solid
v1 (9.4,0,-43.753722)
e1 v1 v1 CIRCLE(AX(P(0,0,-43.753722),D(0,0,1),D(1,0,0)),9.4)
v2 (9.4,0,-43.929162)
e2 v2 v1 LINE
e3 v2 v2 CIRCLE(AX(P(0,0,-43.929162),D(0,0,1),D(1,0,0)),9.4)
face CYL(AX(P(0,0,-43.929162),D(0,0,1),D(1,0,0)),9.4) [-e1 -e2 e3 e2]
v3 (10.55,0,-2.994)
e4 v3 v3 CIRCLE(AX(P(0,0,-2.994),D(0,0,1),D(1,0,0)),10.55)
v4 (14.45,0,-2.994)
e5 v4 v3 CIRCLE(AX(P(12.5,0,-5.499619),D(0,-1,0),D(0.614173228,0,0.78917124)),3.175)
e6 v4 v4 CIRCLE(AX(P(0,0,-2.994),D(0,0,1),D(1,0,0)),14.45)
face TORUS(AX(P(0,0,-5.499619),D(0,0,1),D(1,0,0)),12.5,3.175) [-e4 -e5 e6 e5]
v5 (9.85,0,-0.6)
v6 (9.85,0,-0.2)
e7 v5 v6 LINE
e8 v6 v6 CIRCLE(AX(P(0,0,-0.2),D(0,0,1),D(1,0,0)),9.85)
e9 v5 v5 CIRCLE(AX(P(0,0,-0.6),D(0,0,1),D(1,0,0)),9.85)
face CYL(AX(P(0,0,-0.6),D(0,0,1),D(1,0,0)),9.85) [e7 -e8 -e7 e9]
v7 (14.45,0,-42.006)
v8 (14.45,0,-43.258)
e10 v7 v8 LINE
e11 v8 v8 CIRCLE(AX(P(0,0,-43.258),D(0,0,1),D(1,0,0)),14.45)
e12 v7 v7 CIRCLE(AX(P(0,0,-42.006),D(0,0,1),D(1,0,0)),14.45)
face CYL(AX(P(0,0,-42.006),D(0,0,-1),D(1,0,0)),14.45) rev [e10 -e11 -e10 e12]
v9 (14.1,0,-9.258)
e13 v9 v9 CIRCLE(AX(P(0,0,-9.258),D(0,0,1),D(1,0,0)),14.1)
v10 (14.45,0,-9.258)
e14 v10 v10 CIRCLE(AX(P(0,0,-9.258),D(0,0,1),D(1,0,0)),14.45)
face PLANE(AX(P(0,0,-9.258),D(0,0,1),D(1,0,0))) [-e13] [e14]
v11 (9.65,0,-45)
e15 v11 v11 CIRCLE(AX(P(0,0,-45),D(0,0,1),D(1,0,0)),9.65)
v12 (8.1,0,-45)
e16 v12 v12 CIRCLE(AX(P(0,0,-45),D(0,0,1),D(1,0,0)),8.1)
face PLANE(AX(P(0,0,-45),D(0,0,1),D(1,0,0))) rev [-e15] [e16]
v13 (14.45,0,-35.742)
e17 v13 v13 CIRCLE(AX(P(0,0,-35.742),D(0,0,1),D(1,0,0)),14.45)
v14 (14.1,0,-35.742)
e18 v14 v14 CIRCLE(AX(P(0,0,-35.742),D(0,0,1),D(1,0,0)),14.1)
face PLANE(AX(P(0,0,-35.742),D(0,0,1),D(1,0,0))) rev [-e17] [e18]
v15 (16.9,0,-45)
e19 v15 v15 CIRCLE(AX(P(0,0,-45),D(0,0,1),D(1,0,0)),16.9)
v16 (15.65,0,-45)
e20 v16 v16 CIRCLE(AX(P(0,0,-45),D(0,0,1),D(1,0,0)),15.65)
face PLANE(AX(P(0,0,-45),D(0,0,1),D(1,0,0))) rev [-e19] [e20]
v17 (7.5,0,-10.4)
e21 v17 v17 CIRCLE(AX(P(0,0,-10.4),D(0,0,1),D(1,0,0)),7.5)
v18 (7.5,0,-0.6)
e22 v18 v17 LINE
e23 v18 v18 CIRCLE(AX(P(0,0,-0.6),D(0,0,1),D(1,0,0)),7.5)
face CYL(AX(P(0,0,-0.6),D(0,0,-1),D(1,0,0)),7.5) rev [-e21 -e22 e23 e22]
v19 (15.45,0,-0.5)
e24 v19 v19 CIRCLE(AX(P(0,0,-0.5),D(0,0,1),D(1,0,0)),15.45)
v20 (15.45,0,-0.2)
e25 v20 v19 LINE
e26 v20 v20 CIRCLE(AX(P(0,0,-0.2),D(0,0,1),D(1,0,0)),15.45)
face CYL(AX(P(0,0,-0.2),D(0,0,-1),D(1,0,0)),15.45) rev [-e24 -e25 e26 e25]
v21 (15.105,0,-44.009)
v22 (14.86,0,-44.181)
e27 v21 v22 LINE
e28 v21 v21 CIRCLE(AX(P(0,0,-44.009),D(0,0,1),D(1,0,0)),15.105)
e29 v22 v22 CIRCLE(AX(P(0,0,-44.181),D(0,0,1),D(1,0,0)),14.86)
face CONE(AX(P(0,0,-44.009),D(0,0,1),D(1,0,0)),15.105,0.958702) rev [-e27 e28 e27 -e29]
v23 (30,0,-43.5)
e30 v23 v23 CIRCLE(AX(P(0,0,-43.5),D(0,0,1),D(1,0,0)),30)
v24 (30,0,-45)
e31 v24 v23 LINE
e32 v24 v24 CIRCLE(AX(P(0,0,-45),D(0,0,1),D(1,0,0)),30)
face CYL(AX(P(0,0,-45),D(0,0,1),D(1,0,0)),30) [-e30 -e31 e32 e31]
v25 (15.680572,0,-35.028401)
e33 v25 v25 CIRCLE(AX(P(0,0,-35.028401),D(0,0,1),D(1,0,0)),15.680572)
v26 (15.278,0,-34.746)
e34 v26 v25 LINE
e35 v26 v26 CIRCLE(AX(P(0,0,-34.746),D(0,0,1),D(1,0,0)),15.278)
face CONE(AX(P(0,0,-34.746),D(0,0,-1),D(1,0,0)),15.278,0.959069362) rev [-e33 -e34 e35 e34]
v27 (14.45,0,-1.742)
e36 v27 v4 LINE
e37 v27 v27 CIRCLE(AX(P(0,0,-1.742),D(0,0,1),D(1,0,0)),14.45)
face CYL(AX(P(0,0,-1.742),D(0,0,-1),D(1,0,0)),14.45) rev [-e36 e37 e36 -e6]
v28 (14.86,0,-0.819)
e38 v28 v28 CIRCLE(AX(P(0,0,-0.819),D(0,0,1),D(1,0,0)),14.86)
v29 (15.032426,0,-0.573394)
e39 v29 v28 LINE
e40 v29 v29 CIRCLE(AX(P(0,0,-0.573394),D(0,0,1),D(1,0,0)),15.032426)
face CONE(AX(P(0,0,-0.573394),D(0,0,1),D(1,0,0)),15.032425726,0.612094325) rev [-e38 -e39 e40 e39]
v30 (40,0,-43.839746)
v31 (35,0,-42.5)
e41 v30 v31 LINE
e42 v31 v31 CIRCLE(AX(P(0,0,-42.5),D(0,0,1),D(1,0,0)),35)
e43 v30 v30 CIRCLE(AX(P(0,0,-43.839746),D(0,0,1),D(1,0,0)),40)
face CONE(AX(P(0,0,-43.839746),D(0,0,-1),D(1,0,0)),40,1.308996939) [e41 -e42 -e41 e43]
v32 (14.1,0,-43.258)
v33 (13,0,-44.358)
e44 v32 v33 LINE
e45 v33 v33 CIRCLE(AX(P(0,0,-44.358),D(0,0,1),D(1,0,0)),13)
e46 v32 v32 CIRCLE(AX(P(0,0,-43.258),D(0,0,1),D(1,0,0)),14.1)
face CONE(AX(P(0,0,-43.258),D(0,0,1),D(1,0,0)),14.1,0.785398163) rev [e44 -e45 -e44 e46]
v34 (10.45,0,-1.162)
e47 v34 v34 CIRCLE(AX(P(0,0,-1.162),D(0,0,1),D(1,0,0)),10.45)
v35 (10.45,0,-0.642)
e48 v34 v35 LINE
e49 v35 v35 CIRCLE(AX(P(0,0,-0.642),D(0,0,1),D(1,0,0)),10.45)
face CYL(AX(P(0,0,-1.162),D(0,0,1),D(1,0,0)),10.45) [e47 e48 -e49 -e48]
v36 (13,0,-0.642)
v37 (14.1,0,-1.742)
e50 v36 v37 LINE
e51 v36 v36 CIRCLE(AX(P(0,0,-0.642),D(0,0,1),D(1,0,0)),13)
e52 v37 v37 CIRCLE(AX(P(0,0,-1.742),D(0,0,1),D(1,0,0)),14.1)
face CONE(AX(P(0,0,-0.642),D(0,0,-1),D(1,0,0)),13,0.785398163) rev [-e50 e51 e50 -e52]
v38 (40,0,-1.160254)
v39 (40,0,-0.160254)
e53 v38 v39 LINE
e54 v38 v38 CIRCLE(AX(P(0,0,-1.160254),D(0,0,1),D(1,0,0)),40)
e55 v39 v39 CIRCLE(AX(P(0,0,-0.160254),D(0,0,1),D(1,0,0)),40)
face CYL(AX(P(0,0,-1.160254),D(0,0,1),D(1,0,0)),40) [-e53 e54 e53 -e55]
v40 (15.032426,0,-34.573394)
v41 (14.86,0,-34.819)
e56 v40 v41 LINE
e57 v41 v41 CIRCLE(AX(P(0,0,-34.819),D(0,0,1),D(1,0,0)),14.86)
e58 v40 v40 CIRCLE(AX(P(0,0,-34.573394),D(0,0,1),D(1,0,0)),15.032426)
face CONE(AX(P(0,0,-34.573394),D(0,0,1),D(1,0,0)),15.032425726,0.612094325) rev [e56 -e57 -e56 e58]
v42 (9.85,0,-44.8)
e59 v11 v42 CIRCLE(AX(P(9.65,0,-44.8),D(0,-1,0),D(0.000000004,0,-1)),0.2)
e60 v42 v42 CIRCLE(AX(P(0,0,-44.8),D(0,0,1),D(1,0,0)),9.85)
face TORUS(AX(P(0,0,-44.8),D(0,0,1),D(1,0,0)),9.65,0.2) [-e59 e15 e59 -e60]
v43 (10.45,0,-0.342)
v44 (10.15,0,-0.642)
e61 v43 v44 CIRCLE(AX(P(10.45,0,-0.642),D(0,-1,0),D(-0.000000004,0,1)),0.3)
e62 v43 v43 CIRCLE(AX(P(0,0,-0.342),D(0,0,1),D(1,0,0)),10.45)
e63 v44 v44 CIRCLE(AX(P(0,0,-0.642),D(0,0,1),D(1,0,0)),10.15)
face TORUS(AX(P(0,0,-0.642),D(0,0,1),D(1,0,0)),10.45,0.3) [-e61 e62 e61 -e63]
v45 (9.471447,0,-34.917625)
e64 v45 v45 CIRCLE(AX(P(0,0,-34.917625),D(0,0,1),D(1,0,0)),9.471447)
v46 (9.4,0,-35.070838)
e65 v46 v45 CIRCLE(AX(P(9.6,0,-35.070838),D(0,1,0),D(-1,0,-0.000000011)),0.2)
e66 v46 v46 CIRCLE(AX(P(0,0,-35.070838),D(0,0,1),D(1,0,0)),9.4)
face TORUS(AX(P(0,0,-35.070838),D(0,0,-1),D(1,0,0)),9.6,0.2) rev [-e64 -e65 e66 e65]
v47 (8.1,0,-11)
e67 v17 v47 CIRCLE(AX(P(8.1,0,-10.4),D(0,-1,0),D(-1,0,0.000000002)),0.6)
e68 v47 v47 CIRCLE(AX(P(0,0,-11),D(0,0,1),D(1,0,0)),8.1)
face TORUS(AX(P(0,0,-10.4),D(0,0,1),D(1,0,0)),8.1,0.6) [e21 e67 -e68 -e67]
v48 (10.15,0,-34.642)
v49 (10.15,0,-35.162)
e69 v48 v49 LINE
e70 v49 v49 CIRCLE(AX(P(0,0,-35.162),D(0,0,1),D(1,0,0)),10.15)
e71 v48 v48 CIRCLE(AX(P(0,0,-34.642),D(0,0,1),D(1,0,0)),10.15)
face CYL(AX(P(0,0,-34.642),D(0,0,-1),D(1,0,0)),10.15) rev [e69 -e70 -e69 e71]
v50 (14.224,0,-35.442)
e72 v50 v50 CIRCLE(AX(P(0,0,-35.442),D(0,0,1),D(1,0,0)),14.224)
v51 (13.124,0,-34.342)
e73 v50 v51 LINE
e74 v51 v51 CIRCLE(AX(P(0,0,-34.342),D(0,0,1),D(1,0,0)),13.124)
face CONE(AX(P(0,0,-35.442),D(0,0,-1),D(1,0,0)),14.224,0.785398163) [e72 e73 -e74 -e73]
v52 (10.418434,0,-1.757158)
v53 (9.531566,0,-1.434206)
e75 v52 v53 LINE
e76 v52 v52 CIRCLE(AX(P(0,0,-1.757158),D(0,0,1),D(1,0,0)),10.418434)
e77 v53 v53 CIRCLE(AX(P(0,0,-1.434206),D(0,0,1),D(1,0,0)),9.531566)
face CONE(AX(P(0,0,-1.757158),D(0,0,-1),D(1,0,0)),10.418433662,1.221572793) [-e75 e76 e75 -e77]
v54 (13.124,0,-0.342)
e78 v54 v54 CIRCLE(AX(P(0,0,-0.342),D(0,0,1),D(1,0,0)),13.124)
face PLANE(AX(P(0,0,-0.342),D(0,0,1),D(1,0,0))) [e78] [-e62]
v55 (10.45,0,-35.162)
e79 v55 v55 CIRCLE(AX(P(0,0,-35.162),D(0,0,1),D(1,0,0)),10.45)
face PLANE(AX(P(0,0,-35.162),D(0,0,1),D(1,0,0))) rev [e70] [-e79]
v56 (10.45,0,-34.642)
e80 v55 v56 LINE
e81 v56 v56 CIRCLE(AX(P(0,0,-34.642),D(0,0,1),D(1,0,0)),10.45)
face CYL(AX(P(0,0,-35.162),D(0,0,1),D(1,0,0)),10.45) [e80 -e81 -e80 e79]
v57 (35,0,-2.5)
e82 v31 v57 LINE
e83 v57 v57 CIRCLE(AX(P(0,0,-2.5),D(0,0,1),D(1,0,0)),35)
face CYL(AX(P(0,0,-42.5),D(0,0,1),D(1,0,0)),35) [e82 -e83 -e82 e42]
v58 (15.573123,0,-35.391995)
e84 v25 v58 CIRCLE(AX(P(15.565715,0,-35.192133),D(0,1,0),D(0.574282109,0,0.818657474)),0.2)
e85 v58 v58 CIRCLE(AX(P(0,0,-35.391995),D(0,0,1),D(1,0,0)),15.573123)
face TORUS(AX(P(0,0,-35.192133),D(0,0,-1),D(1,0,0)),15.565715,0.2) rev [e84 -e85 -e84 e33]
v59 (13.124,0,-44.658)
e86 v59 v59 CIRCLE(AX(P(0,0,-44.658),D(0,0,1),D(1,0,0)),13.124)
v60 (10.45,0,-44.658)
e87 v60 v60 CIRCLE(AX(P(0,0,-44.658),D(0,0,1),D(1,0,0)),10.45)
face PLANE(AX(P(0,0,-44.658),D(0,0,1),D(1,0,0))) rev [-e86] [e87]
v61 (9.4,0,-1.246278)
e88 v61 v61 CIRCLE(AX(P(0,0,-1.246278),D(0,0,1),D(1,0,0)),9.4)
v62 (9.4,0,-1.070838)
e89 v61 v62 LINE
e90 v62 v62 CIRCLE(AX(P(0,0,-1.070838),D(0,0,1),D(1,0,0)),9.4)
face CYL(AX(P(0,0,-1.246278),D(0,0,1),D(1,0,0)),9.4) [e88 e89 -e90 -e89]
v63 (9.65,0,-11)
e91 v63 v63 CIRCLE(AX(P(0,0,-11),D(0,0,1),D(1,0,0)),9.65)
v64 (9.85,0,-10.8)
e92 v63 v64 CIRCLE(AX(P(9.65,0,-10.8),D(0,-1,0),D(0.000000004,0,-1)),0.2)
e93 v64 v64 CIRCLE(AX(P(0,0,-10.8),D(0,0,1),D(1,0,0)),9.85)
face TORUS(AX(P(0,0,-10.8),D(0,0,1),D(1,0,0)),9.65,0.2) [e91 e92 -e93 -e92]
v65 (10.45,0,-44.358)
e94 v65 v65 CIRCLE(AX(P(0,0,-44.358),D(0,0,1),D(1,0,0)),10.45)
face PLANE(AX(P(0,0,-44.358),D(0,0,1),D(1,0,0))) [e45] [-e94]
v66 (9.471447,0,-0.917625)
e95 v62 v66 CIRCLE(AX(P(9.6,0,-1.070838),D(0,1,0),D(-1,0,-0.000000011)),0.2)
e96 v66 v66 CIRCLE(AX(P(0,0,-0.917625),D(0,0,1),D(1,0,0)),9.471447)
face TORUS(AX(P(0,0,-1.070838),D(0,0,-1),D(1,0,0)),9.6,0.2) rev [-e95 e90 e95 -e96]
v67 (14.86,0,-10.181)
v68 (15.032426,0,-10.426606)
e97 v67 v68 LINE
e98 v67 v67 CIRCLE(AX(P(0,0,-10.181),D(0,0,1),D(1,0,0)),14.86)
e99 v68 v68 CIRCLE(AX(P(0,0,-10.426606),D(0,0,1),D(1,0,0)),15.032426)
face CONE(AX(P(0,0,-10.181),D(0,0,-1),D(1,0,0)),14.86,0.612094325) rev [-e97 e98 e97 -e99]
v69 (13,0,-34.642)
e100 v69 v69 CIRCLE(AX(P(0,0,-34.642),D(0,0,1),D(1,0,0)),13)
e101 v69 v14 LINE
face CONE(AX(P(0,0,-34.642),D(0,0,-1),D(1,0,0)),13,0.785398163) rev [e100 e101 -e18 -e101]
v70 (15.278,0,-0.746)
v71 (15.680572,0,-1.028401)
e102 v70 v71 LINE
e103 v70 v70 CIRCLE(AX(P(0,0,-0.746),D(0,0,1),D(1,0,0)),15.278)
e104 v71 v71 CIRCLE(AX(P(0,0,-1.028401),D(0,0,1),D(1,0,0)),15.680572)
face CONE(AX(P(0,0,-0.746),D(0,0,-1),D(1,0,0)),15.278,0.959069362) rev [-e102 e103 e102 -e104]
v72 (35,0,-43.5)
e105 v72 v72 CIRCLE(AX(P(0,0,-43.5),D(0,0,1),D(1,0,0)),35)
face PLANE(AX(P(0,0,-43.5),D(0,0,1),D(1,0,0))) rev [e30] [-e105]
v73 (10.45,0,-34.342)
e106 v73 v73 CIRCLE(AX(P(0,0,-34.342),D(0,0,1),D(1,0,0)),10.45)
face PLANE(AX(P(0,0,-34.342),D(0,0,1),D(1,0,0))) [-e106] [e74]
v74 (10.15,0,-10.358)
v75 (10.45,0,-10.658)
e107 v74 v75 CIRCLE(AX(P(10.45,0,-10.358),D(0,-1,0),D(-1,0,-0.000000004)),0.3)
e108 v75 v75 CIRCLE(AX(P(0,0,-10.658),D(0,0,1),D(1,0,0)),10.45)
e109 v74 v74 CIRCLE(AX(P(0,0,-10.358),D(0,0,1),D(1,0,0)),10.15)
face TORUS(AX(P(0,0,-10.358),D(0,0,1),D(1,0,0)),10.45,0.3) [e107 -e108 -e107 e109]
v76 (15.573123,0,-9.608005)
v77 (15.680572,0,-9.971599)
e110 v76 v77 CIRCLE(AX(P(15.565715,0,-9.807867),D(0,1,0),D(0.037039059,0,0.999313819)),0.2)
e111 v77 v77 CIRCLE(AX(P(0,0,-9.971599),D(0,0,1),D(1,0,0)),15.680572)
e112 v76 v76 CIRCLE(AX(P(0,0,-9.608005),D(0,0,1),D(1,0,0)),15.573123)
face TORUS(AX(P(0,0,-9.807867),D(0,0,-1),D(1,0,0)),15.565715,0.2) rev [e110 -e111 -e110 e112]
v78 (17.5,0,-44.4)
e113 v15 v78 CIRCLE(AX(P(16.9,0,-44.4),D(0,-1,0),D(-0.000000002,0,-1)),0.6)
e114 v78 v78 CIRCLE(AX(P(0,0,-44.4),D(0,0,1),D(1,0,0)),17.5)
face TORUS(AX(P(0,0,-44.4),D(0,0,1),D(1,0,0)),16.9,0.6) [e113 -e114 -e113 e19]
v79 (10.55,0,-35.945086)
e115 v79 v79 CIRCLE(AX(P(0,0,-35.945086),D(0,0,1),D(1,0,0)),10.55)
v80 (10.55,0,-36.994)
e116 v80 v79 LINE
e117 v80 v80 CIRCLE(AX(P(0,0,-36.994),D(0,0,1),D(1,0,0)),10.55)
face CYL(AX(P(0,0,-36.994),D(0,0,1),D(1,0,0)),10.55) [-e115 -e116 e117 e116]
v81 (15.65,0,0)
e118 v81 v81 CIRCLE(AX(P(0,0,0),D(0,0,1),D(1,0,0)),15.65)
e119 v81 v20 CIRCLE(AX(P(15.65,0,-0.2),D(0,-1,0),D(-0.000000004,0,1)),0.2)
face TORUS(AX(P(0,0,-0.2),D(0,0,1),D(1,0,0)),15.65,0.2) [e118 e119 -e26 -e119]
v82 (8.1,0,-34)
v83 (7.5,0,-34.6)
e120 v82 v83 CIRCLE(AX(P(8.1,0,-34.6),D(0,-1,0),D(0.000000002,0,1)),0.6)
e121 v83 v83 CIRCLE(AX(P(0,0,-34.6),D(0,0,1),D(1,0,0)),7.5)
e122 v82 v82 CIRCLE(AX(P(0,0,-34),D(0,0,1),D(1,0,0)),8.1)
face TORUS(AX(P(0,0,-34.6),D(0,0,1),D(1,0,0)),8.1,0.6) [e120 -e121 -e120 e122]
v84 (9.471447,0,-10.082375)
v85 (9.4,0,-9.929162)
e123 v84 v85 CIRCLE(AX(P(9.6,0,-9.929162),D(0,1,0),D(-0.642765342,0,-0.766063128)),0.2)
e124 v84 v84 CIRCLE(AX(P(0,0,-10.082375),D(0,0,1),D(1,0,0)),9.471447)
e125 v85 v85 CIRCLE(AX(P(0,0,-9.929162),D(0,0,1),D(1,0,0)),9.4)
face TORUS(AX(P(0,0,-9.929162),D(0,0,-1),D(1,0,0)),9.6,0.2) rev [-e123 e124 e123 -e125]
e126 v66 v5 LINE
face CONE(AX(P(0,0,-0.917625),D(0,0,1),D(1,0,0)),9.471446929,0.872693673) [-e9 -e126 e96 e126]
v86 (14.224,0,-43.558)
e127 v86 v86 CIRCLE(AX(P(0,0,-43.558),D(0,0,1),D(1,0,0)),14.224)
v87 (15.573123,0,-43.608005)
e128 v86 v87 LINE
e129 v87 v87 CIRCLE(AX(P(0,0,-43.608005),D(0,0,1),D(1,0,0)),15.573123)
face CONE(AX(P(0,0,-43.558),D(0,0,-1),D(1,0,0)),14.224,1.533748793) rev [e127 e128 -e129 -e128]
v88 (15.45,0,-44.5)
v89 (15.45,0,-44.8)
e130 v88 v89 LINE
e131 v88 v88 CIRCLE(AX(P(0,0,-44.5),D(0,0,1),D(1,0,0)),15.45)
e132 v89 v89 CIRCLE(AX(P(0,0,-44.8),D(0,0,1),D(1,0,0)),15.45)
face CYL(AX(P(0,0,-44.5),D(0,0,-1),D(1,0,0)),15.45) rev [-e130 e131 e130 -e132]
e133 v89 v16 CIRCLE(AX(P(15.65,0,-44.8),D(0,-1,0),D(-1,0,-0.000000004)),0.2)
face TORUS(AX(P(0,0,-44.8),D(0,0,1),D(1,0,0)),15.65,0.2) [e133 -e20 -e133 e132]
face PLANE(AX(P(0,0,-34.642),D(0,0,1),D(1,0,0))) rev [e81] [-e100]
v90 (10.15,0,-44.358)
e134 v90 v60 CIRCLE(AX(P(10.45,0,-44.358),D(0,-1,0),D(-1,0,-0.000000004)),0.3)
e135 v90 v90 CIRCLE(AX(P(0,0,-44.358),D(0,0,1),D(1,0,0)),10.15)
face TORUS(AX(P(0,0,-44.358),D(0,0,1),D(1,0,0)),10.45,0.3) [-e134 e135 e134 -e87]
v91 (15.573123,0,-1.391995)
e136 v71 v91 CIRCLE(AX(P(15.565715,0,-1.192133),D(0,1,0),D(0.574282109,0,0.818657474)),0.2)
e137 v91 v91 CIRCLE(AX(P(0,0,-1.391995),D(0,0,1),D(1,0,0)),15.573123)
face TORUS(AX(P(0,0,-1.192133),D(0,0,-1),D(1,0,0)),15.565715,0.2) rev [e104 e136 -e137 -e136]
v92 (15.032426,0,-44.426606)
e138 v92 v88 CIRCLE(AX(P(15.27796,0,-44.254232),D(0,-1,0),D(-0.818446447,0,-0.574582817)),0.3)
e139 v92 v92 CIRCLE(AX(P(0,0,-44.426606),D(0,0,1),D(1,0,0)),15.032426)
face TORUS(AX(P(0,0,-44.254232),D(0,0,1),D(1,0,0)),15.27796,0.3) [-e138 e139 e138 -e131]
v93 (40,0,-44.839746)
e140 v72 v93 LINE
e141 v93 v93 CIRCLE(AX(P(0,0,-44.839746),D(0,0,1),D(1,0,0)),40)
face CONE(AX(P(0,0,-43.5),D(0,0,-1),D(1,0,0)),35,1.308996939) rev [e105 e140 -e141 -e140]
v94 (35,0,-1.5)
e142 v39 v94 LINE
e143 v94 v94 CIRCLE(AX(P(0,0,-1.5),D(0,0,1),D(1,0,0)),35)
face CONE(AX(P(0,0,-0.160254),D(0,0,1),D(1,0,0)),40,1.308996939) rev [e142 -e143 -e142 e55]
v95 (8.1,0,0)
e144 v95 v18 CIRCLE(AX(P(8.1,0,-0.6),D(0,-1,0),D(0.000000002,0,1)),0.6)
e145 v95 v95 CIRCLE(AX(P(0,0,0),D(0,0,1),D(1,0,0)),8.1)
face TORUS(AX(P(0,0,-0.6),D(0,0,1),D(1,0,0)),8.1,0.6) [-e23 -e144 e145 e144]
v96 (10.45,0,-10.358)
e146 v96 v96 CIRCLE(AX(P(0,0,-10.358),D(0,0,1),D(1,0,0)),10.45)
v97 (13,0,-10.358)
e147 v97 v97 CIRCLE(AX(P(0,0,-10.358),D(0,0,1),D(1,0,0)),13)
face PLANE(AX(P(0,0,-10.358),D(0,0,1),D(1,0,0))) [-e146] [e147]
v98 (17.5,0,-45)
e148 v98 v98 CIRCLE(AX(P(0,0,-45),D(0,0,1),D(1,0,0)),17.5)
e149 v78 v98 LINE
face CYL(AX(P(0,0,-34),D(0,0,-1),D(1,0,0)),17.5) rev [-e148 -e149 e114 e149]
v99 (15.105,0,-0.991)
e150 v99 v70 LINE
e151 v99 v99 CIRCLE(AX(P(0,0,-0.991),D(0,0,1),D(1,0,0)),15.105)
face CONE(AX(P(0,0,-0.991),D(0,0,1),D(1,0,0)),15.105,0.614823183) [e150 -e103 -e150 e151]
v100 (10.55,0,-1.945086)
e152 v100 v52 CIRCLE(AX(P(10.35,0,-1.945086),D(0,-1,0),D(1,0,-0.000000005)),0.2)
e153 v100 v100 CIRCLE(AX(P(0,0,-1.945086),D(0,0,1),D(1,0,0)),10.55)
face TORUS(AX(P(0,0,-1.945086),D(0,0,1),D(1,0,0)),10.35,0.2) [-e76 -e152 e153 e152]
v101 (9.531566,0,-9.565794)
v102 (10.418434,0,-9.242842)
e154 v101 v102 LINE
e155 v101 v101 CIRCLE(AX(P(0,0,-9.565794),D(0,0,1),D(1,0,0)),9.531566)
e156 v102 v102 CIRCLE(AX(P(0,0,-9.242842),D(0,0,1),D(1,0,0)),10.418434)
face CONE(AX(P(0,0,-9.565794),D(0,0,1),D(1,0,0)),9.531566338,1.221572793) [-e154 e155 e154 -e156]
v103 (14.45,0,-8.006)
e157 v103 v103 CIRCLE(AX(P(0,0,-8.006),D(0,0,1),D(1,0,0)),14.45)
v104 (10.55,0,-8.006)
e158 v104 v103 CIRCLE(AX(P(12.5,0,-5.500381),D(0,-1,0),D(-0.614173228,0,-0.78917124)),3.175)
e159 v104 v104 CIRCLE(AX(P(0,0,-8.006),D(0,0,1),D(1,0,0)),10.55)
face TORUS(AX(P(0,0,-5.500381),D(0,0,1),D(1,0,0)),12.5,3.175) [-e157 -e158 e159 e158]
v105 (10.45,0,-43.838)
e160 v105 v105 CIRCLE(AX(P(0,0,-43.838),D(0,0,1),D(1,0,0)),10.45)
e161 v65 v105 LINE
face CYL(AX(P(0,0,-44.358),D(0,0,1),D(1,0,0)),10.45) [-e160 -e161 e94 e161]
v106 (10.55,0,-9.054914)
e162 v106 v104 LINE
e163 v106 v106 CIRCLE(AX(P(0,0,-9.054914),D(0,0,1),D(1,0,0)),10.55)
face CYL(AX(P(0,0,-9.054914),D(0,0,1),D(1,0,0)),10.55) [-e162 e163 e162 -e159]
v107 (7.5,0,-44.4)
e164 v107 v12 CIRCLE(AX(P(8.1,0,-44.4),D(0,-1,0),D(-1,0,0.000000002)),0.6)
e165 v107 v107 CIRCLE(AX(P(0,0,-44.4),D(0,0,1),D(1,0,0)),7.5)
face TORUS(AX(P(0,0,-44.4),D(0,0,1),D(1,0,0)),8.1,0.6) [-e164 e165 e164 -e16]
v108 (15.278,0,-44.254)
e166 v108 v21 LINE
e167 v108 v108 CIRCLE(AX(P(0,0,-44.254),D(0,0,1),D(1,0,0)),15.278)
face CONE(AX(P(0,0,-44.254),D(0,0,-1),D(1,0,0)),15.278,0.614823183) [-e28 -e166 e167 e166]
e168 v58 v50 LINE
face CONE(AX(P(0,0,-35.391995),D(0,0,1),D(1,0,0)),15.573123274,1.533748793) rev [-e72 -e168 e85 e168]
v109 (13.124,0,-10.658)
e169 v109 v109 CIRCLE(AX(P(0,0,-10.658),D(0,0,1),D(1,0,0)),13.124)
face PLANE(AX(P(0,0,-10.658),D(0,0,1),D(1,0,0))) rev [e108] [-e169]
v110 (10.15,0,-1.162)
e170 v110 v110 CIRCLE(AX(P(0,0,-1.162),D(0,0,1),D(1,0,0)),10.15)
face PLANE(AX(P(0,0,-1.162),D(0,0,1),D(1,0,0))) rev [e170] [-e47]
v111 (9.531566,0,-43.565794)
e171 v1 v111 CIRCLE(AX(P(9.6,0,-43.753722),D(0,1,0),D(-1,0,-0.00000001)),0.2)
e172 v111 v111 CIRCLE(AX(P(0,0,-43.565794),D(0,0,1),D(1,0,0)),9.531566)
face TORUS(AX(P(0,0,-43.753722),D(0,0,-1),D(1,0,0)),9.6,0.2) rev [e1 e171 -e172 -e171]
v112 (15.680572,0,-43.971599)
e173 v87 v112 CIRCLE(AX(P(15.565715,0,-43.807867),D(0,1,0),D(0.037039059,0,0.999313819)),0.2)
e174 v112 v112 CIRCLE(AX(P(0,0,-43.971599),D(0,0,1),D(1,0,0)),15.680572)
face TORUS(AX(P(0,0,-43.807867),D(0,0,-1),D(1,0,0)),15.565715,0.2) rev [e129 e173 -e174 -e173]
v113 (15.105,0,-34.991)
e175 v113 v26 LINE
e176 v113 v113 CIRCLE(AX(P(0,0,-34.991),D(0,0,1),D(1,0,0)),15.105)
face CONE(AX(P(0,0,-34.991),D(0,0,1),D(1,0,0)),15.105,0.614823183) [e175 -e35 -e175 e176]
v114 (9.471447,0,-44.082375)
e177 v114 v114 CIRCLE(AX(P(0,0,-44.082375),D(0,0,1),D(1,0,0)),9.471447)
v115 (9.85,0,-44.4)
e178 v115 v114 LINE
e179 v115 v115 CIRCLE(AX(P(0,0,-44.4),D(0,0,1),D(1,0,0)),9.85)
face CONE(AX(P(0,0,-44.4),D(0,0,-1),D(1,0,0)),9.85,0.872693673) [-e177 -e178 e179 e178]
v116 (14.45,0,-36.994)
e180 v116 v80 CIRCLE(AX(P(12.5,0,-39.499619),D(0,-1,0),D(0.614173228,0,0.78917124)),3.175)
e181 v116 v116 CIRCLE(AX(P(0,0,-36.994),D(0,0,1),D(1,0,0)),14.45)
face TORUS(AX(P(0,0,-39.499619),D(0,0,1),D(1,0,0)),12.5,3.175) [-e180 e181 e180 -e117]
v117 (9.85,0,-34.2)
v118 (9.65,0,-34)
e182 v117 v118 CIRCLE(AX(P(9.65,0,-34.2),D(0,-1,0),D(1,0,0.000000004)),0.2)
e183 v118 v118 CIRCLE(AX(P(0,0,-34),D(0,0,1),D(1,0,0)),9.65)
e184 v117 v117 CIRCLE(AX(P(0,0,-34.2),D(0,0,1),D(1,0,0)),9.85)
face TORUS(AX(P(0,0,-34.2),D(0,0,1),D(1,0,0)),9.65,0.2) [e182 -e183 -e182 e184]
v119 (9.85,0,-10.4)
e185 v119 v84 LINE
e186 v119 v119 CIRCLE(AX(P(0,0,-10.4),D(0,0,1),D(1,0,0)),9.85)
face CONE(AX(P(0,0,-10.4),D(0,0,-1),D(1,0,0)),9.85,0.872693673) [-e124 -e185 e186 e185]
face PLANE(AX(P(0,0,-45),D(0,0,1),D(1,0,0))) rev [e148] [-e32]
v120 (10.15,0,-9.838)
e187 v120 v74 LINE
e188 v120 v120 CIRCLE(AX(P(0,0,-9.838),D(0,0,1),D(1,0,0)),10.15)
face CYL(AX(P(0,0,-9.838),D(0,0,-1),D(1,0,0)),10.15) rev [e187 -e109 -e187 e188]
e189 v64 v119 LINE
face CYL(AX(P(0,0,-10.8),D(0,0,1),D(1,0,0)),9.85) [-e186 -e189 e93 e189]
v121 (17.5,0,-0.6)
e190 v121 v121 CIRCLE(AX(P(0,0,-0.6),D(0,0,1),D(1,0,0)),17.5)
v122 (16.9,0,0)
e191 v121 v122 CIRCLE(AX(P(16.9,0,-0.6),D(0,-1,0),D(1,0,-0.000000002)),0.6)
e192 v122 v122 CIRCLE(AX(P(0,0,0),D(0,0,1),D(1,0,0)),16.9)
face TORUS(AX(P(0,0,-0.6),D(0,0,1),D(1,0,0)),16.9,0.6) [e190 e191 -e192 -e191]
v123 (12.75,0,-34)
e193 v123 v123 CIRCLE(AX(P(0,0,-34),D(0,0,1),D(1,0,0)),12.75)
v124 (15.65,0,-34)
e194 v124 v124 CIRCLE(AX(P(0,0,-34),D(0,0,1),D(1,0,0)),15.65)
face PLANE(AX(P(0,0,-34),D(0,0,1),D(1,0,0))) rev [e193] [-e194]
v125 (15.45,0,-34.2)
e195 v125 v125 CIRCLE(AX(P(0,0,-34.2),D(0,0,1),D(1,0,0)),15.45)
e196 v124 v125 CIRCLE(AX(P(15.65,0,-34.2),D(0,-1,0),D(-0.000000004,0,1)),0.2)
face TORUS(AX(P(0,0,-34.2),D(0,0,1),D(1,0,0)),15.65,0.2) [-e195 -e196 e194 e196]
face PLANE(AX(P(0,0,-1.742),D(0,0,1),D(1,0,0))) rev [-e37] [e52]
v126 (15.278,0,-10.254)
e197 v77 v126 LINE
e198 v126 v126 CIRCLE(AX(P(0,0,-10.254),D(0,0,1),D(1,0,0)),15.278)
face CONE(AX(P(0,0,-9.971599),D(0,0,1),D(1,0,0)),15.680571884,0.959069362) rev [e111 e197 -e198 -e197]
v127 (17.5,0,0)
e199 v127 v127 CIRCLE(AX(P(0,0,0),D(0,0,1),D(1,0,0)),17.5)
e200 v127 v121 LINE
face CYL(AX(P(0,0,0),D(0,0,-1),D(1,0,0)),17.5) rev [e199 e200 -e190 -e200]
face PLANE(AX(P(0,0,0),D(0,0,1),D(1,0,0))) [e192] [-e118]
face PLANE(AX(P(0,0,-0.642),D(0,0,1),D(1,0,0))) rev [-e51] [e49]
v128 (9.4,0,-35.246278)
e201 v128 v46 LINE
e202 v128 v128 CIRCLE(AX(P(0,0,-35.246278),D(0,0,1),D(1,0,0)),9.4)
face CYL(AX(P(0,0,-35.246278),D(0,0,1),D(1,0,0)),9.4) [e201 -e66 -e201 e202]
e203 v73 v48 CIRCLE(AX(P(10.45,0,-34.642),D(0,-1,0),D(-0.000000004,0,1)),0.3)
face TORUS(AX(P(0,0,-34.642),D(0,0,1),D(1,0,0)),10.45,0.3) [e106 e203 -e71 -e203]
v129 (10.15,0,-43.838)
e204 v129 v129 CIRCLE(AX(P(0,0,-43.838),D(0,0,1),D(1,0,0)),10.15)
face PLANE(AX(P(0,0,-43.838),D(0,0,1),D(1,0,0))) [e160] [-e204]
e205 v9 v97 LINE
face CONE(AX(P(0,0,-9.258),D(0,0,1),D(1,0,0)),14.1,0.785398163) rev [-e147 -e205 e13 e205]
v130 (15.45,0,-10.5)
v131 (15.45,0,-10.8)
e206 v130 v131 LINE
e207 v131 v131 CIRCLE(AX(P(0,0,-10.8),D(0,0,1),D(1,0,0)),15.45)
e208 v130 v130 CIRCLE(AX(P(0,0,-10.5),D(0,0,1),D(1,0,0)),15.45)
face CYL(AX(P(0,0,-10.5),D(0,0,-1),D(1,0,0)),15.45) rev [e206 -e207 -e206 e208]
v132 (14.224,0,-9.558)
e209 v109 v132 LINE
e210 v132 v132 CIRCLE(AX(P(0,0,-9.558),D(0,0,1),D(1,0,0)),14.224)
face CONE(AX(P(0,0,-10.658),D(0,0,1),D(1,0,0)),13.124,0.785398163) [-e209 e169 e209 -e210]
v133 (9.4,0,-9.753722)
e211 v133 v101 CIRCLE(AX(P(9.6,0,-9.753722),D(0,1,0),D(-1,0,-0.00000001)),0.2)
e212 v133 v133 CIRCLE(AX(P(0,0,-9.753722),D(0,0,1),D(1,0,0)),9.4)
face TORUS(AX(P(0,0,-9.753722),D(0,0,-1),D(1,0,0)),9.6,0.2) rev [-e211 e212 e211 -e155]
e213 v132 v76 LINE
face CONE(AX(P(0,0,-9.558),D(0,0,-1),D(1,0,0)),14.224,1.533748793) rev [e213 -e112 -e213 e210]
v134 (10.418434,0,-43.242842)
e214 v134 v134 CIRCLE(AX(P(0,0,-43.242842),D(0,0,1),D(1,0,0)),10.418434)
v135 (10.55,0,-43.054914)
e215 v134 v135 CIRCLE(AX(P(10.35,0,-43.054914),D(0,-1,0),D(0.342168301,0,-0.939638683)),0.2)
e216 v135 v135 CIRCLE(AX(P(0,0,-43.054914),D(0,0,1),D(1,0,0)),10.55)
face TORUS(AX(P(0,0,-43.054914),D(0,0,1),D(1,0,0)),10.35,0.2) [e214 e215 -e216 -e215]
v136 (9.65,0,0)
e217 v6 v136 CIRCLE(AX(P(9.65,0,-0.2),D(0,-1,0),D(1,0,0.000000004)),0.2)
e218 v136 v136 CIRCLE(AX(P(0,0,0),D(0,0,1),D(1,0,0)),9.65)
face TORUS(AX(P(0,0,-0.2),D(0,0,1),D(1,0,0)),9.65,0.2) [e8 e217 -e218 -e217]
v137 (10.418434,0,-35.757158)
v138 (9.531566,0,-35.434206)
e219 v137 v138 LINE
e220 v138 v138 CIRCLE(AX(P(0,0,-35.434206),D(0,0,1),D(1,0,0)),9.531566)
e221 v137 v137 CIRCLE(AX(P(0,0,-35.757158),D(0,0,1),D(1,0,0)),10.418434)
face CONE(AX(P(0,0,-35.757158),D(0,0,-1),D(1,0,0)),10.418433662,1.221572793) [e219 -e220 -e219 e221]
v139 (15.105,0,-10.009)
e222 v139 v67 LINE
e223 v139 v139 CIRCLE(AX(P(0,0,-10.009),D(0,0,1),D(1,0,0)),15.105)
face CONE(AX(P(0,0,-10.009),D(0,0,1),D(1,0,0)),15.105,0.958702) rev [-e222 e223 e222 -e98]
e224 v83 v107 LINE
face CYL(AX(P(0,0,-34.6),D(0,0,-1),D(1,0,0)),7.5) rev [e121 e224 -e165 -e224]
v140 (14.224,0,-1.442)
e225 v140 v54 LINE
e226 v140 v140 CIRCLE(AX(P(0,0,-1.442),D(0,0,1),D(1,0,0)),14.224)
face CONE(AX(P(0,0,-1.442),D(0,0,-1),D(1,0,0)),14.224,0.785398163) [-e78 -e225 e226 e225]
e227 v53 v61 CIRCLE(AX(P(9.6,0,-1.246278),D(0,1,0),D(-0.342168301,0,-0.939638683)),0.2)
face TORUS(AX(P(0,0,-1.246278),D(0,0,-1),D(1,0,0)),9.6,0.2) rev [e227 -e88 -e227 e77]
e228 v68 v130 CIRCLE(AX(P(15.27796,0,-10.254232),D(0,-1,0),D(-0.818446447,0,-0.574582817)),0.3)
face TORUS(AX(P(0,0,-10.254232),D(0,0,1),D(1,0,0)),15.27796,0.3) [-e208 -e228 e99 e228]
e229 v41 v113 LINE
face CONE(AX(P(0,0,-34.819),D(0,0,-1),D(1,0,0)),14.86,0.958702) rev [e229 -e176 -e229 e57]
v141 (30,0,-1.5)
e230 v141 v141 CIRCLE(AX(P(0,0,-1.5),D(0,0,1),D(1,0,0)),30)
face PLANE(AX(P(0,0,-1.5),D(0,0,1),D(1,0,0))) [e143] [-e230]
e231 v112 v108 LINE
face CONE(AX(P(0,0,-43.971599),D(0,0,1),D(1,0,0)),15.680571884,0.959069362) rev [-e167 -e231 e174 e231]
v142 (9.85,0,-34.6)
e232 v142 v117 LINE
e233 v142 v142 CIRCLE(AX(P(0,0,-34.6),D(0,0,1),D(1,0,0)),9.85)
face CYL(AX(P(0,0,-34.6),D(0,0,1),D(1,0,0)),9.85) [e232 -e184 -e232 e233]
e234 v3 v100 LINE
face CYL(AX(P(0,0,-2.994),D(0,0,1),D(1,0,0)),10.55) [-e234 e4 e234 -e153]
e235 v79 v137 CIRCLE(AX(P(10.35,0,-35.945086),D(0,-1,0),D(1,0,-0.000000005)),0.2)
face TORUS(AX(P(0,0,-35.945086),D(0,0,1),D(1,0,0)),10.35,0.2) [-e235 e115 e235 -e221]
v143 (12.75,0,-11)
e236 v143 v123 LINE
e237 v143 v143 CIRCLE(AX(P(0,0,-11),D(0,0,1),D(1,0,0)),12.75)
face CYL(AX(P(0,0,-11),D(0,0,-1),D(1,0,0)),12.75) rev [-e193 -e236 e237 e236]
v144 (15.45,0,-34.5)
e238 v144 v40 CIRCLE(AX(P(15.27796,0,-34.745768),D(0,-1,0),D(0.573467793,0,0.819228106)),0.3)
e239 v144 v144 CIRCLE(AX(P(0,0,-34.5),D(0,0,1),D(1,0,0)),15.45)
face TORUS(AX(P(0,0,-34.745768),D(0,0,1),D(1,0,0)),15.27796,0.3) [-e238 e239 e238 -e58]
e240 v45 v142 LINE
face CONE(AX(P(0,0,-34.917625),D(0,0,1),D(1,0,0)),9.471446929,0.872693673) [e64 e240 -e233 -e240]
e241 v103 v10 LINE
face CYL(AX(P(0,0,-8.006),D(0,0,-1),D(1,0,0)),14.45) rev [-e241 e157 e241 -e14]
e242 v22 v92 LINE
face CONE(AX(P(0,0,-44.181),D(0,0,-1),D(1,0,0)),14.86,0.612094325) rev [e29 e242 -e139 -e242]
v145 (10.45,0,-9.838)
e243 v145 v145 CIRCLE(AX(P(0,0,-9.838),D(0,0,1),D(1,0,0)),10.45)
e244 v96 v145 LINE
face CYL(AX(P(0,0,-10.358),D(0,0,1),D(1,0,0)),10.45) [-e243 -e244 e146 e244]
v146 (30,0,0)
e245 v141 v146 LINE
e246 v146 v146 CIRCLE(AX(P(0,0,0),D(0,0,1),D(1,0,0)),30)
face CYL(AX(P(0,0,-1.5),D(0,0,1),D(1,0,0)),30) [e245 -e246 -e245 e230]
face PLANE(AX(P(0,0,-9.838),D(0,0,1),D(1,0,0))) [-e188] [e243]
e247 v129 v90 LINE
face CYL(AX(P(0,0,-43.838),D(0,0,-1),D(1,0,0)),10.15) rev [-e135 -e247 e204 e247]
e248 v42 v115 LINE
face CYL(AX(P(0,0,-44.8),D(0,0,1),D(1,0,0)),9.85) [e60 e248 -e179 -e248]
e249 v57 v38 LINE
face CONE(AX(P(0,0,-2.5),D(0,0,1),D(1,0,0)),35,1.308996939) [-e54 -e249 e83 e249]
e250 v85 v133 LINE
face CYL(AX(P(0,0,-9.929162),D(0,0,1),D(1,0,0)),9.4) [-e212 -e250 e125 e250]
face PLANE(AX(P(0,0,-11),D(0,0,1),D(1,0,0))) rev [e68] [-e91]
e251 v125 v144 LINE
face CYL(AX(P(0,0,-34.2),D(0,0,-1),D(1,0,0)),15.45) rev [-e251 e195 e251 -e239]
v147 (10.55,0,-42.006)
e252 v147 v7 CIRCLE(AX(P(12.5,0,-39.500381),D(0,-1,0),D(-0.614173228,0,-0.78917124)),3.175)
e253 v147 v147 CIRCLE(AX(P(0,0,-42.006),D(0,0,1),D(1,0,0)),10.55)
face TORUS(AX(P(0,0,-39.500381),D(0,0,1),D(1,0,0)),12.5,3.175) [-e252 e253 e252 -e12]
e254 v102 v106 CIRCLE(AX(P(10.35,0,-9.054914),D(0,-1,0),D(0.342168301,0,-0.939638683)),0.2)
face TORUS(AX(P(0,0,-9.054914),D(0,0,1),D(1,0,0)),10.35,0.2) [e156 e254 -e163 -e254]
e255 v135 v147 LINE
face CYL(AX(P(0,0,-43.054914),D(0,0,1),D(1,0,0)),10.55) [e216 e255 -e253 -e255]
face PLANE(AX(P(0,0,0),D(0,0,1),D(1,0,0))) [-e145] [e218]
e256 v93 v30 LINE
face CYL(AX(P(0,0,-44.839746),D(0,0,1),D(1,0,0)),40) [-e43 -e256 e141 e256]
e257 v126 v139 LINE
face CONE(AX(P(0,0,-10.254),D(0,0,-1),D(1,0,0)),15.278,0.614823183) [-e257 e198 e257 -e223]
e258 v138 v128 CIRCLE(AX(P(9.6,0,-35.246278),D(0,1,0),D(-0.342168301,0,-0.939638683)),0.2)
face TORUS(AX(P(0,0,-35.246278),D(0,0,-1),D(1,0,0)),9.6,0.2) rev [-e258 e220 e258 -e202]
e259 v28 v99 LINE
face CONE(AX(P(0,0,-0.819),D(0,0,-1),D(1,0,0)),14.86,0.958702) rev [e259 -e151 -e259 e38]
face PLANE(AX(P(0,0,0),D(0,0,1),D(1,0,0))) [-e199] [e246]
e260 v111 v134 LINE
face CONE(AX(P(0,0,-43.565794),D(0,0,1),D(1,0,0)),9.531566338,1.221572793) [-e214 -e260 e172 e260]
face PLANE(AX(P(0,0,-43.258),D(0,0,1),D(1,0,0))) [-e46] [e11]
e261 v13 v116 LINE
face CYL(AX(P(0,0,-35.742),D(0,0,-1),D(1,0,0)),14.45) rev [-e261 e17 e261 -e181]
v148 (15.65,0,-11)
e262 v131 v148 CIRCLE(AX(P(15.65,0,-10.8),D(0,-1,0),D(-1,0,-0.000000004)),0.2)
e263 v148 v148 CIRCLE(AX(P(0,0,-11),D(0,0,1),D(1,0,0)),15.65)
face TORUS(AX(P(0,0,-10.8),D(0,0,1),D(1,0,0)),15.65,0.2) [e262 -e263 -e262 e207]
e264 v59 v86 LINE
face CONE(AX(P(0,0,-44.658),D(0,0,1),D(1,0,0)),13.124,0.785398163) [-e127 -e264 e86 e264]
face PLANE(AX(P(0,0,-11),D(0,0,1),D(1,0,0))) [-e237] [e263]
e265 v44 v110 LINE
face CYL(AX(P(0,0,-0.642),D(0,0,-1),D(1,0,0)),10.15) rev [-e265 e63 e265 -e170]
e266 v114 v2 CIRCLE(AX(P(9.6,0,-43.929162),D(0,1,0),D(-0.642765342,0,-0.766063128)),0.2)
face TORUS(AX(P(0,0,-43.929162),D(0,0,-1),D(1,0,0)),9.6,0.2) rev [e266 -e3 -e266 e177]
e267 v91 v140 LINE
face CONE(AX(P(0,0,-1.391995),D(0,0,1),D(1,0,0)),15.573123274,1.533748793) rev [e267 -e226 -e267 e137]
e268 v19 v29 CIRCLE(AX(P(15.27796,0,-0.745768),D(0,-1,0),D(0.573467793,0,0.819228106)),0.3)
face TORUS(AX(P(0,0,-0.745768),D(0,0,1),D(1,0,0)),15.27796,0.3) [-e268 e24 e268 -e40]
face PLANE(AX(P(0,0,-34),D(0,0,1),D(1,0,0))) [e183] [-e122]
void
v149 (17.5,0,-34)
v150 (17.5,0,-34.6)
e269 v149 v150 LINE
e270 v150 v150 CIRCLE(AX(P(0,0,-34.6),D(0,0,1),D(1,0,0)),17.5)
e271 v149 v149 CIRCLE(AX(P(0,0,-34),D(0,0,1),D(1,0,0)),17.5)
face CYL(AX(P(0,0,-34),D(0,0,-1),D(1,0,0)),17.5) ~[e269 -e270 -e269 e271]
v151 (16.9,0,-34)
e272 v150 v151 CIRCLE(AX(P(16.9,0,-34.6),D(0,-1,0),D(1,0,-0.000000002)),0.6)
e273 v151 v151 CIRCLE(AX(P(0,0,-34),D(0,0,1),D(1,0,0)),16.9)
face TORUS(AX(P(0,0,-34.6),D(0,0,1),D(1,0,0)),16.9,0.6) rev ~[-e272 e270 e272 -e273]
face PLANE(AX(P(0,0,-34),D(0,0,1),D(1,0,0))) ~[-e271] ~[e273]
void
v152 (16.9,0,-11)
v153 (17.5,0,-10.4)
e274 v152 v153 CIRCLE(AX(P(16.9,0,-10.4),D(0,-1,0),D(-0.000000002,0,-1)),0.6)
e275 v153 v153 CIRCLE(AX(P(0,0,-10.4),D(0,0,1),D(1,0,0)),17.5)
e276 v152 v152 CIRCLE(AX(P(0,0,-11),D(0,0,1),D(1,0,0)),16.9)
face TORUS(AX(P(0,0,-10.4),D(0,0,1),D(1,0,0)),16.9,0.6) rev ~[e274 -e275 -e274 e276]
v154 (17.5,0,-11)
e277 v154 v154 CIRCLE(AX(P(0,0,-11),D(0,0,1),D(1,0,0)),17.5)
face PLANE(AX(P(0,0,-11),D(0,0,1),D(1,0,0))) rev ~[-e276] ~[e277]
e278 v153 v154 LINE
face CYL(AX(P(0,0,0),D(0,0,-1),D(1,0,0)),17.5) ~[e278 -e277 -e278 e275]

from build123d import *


with BuildPart() as part:
    # 草图1 → 旋转1 (revolve)
    with BuildSketch(Plane(origin=(0, 0, 0), x_dir=(0, 0, -1), z_dir=(1, 0, 0)), mode=Mode.PRIVATE) as revolve_1_sk:
        Polygon((0, 17.5), (11, 17.5), (11, 12.75), (34, 12.75), (34, 17.5), (45, 17.5), (45, 30), (43.5, 30), (43.5, 35), (44.839745962, 40), (43.839745962, 40), (42.5, 35), (2.5, 35), (1.160254038, 40), (0.160254038, 40), (1.5, 35), (1.5, 30), (0, 30), align=None)
    revolve(revolve_1_sk.sketch.rotate(Axis((0, 0, -45), (0, 0, 1)), 270), axis=Axis((0, 0, -45), (0, 0, 1)))

    # 草图2 → 旋转2 (revolve)
    with BuildSketch(Plane(origin=(0, 0, 0), x_dir=(0, 0, -1), z_dir=(1, 0, 0)), mode=Mode.PRIVATE) as revolve_2_sk:
        with BuildLine():
            Line((0.2, 15.45), (0.5, 15.45))
            ThreePointArc((0.5, 15.45), (0.45029759, 15.226027188), (0.573393587, 15.032425726))
            Line((0.573393587, 15.032425726), (0.819, 14.86))
            Line((0.819, 14.86), (0.991, 15.105))
            Line((0.991, 15.105), (0.746, 15.278))
            Line((0.746, 15.278), (1.028401172, 15.680571884))
            ThreePointArc((1.028401172, 15.680571884), (1.24881307, 15.757515702), (1.391995431, 15.573123274))
            Line((1.391995431, 15.573123274), (1.442, 14.224))
            Line((1.442, 14.224), (0.342, 13.124))
            Line((0.342, 13.124), (0.342, 10.45))
            ThreePointArc((0.342, 10.45), (0.429867966, 10.237867966), (0.642, 10.15))
            Line((0.642, 10.15), (1.162, 10.15))
            Line((1.162, 10.15), (1.162, 10.45))
            Line((1.162, 10.45), (0.642, 10.45))
            Line((0.642, 10.45), (0.642, 13))
            Line((0.642, 13), (1.742, 14.1))
            Line((1.742, 14.1), (1.742, 14.45))
            Line((1.742, 14.45), (2.994, 14.45))
            ThreePointArc((2.994, 14.45), (2.324618686, 12.5), (2.994, 10.55))
            Line((2.994, 10.55), (1.945085653, 10.55))
            ThreePointArc((1.945085653, 10.55), (1.830383283, 10.513839453), (1.757157918, 10.418433662))
            Line((1.757157918, 10.418433662), (1.434206231, 9.531566338))
            ThreePointArc((1.434206231, 9.531566338), (1.360980866, 9.436160547), (1.246278495, 9.4))
            Line((1.246278495, 9.4), (1.070837627, 9.4))
            ThreePointArc((1.070837627, 9.4), (0.986311342, 9.41873967), (0.917625005, 9.471446929))
            Line((0.917625005, 9.471446929), (0.6, 9.85))
            Line((0.6, 9.85), (0.2, 9.85))
            ThreePointArc((0.2, 9.85), (0.058578644, 9.791421356), (0, 9.65))
            Line((0, 9.65), (0, 8.1))
            ThreePointArc((0, 8.1), (0.175735931, 7.675735931), (0.6, 7.5))
            Line((0.6, 7.5), (10.4, 7.5))
            ThreePointArc((10.4, 7.5), (10.824264069, 7.675735931), (11, 8.1))
            Line((11, 8.1), (11, 9.65))
            ThreePointArc((11, 9.65), (10.941421356, 9.791421356), (10.8, 9.85))
            Line((10.8, 9.85), (10.4, 9.85))
            Line((10.4, 9.85), (10.082374995, 9.471446929))
            ThreePointArc((10.082374995, 9.471446929), (10.013688658, 9.41873967), (9.929162373, 9.4))
            Line((9.929162373, 9.4), (9.753721505, 9.4))
            ThreePointArc((9.753721505, 9.4), (9.639019134, 9.436160547), (9.565793769, 9.531566338))
            Line((9.565793769, 9.531566338), (9.242842082, 10.418433662))
            ThreePointArc((9.242842082, 10.418433662), (9.169616717, 10.513839453), (9.054914347, 10.55))
            Line((9.054914347, 10.55), (8.006, 10.55))
            ThreePointArc((8.006, 10.55), (8.675381314, 12.5), (8.006, 14.45))
            Line((8.006, 14.45), (9.258, 14.45))
            Line((9.258, 14.45), (9.258, 14.1))
            Line((9.258, 14.1), (10.358, 13))
            Line((10.358, 13), (10.358, 10.45))
            Line((10.358, 10.45), (9.838, 10.45))
            Line((9.838, 10.45), (9.838, 10.15))
            Line((9.838, 10.15), (10.358, 10.15))
            ThreePointArc((10.358, 10.15), (10.570132034, 10.237867966), (10.658, 10.45))
            Line((10.658, 10.45), (10.658, 13.124))
            Line((10.658, 13.124), (9.558, 14.224))
            Line((9.558, 14.224), (9.608004569, 15.573123274))
            ThreePointArc((9.608004569, 15.573123274), (9.75118693, 15.757515702), (9.971598828, 15.680571884))
            Line((9.971598828, 15.680571884), (10.254, 15.278))
            Line((10.254, 15.278), (10.009, 15.105))
            Line((10.009, 15.105), (10.181, 14.86))
            Line((10.181, 14.86), (10.426606413, 15.032425726))
            ThreePointArc((10.426606413, 15.032425726), (10.54970241, 15.226027188), (10.5, 15.45))
            Line((10.5, 15.45), (10.8, 15.45))
            ThreePointArc((10.8, 15.45), (10.941421356, 15.508578644), (11, 15.65))
            Line((11, 15.65), (11, 16.9))
            ThreePointArc((11, 16.9), (10.824264069, 17.324264069), (10.4, 17.5))
            Line((10.4, 17.5), (0.6, 17.5))
            ThreePointArc((0.6, 17.5), (0.175735931, 17.324264069), (0, 16.9))
            Line((0, 16.9), (0, 15.65))
            ThreePointArc((0, 15.65), (0.058578644, 15.508578644), (0.2, 15.45))
        make_face()
    revolve(revolve_2_sk.sketch.rotate(Axis((0, 0, -50), (0, 0, 1)), 270), axis=Axis((0, 0, -50), (0, 0, 1)))

    # 草图3 → 旋转3 (revolve)
    with BuildSketch(Plane(origin=(0, 0, 0), x_dir=(0, 0, -1), z_dir=(1, 0, 0)), mode=Mode.PRIVATE) as revolve_3_sk:
        with BuildLine():
            Line((34.2, 15.45), (34.5, 15.45))
            ThreePointArc((34.5, 15.45), (34.45029759, 15.226027188), (34.573393587, 15.032425726))
            Line((34.573393587, 15.032425726), (34.819, 14.86))
            Line((34.819, 14.86), (34.991, 15.105))
            Line((34.991, 15.105), (34.746, 15.278))
            Line((34.746, 15.278), (35.028401172, 15.680571884))
            ThreePointArc((35.028401172, 15.680571884), (35.24881307, 15.757515702), (35.391995431, 15.573123274))
            Line((35.391995431, 15.573123274), (35.442, 14.224))
            Line((35.442, 14.224), (34.342, 13.124))
            Line((34.342, 13.124), (34.342, 10.45))
            ThreePointArc((34.342, 10.45), (34.429867966, 10.237867966), (34.642, 10.15))
            Line((34.642, 10.15), (35.162, 10.15))
            Line((35.162, 10.15), (35.162, 10.45))
            Line((35.162, 10.45), (34.642, 10.45))
            Line((34.642, 10.45), (34.642, 13))
            Line((34.642, 13), (35.742, 14.1))
            Line((35.742, 14.1), (35.742, 14.45))
            Line((35.742, 14.45), (36.994, 14.45))
            ThreePointArc((36.994, 14.45), (36.324618686, 12.5), (36.994, 10.55))
            Line((36.994, 10.55), (35.945085653, 10.55))
            ThreePointArc((35.945085653, 10.55), (35.830383283, 10.513839453), (35.757157918, 10.418433662))
            Line((35.757157918, 10.418433662), (35.434206231, 9.531566338))
            ThreePointArc((35.434206231, 9.531566338), (35.360980866, 9.436160547), (35.246278495, 9.4))
            Line((35.246278495, 9.4), (35.070837627, 9.4))
            ThreePointArc((35.070837627, 9.4), (34.986311342, 9.41873967), (34.917625005, 9.471446929))
            Line((34.917625005, 9.471446929), (34.6, 9.85))
            Line((34.6, 9.85), (34.2, 9.85))
            ThreePointArc((34.2, 9.85), (34.058578644, 9.791421356), (34, 9.65))
            Line((34, 9.65), (34, 8.1))
            ThreePointArc((34, 8.1), (34.175735931, 7.675735931), (34.6, 7.5))
            Line((34.6, 7.5), (44.4, 7.5))
            ThreePointArc((44.4, 7.5), (44.824264069, 7.675735931), (45, 8.1))
            Line((45, 8.1), (45, 9.65))
            ThreePointArc((45, 9.65), (44.941421356, 9.791421356), (44.8, 9.85))
            Line((44.8, 9.85), (44.4, 9.85))
            Line((44.4, 9.85), (44.082374995, 9.471446929))
            ThreePointArc((44.082374995, 9.471446929), (44.013688658, 9.41873967), (43.929162373, 9.4))
            Line((43.929162373, 9.4), (43.753721505, 9.4))
            ThreePointArc((43.753721505, 9.4), (43.639019134, 9.436160547), (43.565793769, 9.531566338))
            Line((43.565793769, 9.531566338), (43.242842082, 10.418433662))
            ThreePointArc((43.242842082, 10.418433662), (43.169616717, 10.513839453), (43.054914347, 10.55))
            Line((43.054914347, 10.55), (42.006, 10.55))
            ThreePointArc((42.006, 10.55), (42.675381314, 12.5), (42.006, 14.45))
            Line((42.006, 14.45), (43.258, 14.45))
            Line((43.258, 14.45), (43.258, 14.1))
            Line((43.258, 14.1), (44.358, 13))
            Line((44.358, 13), (44.358, 10.45))
            Line((44.358, 10.45), (43.838, 10.45))
            Line((43.838, 10.45), (43.838, 10.15))
            Line((43.838, 10.15), (44.358, 10.15))
            ThreePointArc((44.358, 10.15), (44.570132034, 10.237867966), (44.658, 10.45))
            Line((44.658, 10.45), (44.658, 13.124))
            Line((44.658, 13.124), (43.558, 14.224))
            Line((43.558, 14.224), (43.608004569, 15.573123274))
            ThreePointArc((43.608004569, 15.573123274), (43.75118693, 15.757515702), (43.971598828, 15.680571884))
            Line((43.971598828, 15.680571884), (44.254, 15.278))
            Line((44.254, 15.278), (44.009, 15.105))
            Line((44.009, 15.105), (44.181, 14.86))
            Line((44.181, 14.86), (44.426606413, 15.032425726))
            ThreePointArc((44.426606413, 15.032425726), (44.54970241, 15.226027188), (44.5, 15.45))
            Line((44.5, 15.45), (44.8, 15.45))
            ThreePointArc((44.8, 15.45), (44.941421356, 15.508578644), (45, 15.65))
            Line((45, 15.65), (45, 16.9))
            ThreePointArc((45, 16.9), (44.824264069, 17.324264069), (44.4, 17.5))
            Line((44.4, 17.5), (34.6, 17.5))
            ThreePointArc((34.6, 17.5), (34.175735931, 17.324264069), (34, 16.9))
            Line((34, 16.9), (34, 15.65))
            ThreePointArc((34, 15.65), (34.058578644, 15.508578644), (34.2, 15.45))
        make_face()
    revolve(revolve_3_sk.sketch.rotate(Axis((0, 0, -50), (0, 0, 1)), 270), axis=Axis((0, 0, -50), (0, 0, 1)))


solid = part.part
